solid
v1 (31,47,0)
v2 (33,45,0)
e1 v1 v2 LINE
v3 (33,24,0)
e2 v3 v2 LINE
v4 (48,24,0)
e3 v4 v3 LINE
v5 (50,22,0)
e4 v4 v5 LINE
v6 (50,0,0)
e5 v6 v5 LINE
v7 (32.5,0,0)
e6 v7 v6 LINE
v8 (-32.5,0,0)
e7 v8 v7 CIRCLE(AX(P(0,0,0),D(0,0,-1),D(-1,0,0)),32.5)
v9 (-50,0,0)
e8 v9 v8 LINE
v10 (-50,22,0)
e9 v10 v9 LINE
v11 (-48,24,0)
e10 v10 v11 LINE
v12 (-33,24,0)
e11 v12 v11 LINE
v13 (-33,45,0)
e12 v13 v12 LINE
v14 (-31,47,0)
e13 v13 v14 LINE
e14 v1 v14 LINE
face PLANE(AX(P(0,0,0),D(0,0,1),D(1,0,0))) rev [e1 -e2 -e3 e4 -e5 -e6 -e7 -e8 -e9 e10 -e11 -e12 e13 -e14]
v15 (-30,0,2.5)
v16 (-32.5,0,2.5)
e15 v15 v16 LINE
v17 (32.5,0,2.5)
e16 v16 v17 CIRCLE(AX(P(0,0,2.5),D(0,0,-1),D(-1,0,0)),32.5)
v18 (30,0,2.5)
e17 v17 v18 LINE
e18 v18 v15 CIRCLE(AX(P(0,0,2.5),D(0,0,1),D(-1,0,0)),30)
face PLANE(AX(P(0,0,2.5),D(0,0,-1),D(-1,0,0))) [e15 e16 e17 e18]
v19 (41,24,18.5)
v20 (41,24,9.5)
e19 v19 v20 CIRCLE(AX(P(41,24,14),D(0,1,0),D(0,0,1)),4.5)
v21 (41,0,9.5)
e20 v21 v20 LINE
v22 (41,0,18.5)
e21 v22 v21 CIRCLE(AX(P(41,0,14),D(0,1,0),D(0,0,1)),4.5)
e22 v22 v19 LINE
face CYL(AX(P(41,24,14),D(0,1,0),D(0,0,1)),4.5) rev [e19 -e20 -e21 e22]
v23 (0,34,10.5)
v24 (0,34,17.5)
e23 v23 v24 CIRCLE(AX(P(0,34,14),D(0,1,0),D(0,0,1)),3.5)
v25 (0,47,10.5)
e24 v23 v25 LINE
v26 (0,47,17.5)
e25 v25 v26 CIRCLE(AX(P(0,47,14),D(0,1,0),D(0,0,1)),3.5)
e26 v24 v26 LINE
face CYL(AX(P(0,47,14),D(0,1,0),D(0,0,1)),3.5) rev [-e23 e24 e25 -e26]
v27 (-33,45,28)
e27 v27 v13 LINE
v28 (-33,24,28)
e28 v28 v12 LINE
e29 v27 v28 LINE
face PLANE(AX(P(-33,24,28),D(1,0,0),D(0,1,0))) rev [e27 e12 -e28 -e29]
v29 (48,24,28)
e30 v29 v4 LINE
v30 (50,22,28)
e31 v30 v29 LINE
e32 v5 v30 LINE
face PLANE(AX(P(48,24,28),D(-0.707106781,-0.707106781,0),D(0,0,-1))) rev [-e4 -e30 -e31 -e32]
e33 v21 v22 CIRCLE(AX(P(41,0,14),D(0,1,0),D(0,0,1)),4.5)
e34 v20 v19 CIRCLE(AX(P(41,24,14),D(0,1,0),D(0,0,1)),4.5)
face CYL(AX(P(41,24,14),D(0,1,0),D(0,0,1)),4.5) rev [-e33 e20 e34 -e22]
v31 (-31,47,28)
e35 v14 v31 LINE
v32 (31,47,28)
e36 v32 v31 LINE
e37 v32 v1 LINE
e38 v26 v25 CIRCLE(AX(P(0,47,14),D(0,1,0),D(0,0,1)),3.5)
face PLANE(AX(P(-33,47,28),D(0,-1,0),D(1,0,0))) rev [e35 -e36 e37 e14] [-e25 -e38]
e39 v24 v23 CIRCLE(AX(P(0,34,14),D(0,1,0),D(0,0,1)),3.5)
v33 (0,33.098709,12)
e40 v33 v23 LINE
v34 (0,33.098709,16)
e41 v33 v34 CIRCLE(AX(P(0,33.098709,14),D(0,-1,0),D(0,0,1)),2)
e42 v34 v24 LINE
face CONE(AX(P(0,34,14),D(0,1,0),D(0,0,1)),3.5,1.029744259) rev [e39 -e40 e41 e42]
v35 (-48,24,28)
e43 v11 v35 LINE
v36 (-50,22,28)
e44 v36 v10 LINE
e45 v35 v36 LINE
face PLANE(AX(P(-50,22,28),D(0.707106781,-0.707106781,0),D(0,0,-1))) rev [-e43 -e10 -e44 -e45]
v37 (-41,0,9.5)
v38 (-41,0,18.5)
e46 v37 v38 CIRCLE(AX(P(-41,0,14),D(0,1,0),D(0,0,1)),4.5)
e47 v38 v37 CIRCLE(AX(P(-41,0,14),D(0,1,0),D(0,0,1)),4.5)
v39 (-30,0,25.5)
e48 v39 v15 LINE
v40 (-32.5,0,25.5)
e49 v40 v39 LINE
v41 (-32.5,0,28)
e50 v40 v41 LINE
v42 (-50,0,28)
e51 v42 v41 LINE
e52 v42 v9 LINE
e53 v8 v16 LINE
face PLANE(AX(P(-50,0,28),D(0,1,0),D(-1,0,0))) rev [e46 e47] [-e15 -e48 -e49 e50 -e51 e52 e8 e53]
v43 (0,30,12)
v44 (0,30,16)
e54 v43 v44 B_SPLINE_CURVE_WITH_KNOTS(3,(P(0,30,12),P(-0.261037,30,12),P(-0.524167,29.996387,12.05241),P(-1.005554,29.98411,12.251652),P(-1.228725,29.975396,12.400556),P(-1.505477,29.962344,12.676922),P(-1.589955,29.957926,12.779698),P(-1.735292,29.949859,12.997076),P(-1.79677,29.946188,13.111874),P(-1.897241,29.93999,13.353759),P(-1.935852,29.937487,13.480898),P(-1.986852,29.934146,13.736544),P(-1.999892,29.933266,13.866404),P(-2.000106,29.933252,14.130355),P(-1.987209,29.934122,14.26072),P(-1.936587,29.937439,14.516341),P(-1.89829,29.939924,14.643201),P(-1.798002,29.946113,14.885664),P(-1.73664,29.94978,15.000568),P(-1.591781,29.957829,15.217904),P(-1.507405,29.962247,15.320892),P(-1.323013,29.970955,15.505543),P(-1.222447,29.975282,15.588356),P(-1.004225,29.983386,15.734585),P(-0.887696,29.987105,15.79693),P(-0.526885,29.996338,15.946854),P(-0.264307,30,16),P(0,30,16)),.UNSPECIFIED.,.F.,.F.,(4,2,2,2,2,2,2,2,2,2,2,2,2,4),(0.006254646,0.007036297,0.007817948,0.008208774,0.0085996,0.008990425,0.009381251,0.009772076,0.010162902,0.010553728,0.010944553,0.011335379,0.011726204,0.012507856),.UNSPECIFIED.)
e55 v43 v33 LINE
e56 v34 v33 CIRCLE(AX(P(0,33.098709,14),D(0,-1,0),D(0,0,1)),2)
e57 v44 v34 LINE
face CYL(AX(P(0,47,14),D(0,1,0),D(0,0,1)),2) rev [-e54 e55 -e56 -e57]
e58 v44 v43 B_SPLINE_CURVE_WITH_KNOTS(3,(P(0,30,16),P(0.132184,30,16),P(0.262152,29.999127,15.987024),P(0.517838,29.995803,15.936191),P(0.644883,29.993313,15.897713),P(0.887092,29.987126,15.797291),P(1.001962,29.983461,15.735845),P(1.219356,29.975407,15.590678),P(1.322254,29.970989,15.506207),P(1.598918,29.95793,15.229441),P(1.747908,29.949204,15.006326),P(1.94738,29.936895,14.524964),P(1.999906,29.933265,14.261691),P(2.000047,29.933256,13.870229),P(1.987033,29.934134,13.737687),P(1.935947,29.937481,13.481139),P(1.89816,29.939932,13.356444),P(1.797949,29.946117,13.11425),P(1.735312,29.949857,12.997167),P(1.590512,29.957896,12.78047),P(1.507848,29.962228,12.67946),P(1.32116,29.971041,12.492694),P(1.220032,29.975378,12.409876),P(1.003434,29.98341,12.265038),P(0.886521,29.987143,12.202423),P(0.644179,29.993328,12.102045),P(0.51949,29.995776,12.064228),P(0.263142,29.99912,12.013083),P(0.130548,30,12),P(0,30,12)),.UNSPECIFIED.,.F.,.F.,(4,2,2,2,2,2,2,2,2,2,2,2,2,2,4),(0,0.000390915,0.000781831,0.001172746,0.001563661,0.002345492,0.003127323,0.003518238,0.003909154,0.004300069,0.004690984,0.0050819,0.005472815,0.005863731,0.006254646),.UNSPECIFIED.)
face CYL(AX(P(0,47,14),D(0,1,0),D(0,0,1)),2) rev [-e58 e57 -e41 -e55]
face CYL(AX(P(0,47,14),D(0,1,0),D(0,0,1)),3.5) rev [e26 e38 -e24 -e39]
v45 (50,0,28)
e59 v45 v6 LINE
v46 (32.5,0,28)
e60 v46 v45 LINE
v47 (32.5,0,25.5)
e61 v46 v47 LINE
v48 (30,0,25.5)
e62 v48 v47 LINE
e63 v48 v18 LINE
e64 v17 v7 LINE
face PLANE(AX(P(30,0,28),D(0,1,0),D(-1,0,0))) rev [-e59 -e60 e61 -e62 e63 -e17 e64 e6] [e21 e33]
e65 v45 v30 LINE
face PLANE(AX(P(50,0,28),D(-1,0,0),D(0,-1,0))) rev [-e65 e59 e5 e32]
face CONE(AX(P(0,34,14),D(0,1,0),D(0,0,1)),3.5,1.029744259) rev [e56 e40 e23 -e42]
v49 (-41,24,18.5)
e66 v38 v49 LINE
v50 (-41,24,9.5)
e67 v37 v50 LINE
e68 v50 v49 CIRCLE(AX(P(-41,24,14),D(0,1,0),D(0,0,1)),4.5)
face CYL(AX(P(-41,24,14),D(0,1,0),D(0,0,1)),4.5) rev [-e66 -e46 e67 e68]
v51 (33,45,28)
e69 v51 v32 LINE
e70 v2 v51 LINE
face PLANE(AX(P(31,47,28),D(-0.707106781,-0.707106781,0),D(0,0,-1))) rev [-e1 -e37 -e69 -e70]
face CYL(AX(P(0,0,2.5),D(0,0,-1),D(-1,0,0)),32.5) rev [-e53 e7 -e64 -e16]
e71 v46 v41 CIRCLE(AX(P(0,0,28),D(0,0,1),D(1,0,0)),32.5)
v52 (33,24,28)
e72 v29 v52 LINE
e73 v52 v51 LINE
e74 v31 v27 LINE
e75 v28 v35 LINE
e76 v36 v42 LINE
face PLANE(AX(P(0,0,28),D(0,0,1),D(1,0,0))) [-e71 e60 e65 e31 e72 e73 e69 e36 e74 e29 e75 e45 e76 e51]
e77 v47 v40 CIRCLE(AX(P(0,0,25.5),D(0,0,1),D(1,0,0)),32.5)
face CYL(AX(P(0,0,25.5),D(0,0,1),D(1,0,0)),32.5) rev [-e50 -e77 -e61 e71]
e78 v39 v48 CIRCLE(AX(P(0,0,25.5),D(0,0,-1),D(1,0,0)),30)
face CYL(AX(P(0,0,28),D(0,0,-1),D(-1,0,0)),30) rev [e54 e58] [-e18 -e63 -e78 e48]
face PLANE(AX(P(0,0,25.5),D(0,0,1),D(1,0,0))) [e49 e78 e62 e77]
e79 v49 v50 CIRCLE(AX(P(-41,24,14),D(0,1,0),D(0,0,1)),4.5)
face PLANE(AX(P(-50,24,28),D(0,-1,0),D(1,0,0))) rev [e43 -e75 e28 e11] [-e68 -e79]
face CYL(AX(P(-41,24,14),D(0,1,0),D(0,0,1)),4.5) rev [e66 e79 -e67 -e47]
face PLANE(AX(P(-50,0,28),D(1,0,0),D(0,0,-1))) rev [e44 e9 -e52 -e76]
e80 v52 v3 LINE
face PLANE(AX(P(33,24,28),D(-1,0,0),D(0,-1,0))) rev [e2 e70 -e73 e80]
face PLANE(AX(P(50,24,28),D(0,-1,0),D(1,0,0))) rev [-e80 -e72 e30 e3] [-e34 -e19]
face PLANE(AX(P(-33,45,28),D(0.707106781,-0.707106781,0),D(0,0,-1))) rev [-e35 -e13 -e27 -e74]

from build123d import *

# Parameters (mm, degrees)
BOSS_EXTRUDE1_DEPTH       = 28
CHAMFER1_SIZE             = 2
M8X1_0_TAPPED_HOLE1_D     = 7
M8X1_0_TAPPED_HOLE1_DEPTH = 13
M8X1_0_TAPPED_HOLE1_TIP   = 2.103012167
HOLE2_D                   = 9
SKETCH15_R                = 32.5
CUT_EXTRUDE3_DEPTH        = 2.5
CUT_EXTRUDE4_START        = -2.5
SKETCH16_R                = 32.5
CUT_EXTRUDE4_DEPTH        = 2.5
HOLE3_D                   = 4


with BuildPart() as part:
    # Sketch1 → Boss-Extrude1 (new body)
    with BuildSketch(Plane.XY):
        with BuildLine():
            Line((-50, 24), (-33, 24))
            Line((-33, 24), (-33, 47))
            Line((-33, 47), (33, 47))
            Line((33, 47), (33, 24))
            Line((33, 24), (50, 24))
            Line((50, 24), (50, 0))
            Line((50, 0), (30, 0))
            ThreePointArc((30, 0), (0, 30), (-30, 0))
            Line((-30, 0), (-50, 0))
            Line((-50, 0), (-50, 24))
        make_face()
    extrude(amount=BOSS_EXTRUDE1_DEPTH)

    # Chamfer1
    chamfer1_edges = [part.edges().sort_by_distance(p)[0] for p in [
        (-50, 24, 14),
        (-33, 47, 14),
        (33, 47, 14),
        (50, 24, 14),
    ]]
    chamfer(chamfer1_edges, length=CHAMFER1_SIZE)

    # M8x1.0 Tapped Hole1
    with Locations(Plane(origin=(0, 47, 0), x_dir=(1, 0, 0), z_dir=(0, 1, 0))):
        with Locations((0, -14)):
            Hole(M8X1_0_TAPPED_HOLE1_D / 2, depth=M8X1_0_TAPPED_HOLE1_DEPTH)
            with Locations((0, 0, -(M8X1_0_TAPPED_HOLE1_DEPTH + M8X1_0_TAPPED_HOLE1_TIP / 2))):  # 118° drill point
                Cone(0, M8X1_0_TAPPED_HOLE1_D / 2, M8X1_0_TAPPED_HOLE1_TIP, mode=Mode.SUBTRACT)

    # Hole2 (through all)
    with Locations(Plane(origin=(0, 24, 0), x_dir=(1, 0, 0), z_dir=(0, 1, 0))):
        with Locations((-41, -14), (41, -14)):
            Hole(HOLE2_D / 2)

    # Sketch15 → Cut-Extrude3 (cut)
    with BuildSketch(Plane(origin=(0, 0, 0), x_dir=(-1, 0, 0), z_dir=(0, 0, -1))):
        Circle(SKETCH15_R)
    extrude(amount=-CUT_EXTRUDE3_DEPTH, mode=Mode.SUBTRACT)

    # Sketch16 → Cut-Extrude4 (cut)
    with BuildSketch(Plane.XY.offset(28).offset(CUT_EXTRUDE4_START)):
        Circle(SKETCH16_R)
    extrude(amount=CUT_EXTRUDE4_DEPTH, mode=Mode.SUBTRACT)

    # Hole3 (through all)
    with Locations(Plane(origin=(0, 47, 0), x_dir=(1, 0, 0), z_dir=(0, 1, 0))):
        with Locations((0, -14)):
            Hole(HOLE3_D / 2)


solid = part.part
